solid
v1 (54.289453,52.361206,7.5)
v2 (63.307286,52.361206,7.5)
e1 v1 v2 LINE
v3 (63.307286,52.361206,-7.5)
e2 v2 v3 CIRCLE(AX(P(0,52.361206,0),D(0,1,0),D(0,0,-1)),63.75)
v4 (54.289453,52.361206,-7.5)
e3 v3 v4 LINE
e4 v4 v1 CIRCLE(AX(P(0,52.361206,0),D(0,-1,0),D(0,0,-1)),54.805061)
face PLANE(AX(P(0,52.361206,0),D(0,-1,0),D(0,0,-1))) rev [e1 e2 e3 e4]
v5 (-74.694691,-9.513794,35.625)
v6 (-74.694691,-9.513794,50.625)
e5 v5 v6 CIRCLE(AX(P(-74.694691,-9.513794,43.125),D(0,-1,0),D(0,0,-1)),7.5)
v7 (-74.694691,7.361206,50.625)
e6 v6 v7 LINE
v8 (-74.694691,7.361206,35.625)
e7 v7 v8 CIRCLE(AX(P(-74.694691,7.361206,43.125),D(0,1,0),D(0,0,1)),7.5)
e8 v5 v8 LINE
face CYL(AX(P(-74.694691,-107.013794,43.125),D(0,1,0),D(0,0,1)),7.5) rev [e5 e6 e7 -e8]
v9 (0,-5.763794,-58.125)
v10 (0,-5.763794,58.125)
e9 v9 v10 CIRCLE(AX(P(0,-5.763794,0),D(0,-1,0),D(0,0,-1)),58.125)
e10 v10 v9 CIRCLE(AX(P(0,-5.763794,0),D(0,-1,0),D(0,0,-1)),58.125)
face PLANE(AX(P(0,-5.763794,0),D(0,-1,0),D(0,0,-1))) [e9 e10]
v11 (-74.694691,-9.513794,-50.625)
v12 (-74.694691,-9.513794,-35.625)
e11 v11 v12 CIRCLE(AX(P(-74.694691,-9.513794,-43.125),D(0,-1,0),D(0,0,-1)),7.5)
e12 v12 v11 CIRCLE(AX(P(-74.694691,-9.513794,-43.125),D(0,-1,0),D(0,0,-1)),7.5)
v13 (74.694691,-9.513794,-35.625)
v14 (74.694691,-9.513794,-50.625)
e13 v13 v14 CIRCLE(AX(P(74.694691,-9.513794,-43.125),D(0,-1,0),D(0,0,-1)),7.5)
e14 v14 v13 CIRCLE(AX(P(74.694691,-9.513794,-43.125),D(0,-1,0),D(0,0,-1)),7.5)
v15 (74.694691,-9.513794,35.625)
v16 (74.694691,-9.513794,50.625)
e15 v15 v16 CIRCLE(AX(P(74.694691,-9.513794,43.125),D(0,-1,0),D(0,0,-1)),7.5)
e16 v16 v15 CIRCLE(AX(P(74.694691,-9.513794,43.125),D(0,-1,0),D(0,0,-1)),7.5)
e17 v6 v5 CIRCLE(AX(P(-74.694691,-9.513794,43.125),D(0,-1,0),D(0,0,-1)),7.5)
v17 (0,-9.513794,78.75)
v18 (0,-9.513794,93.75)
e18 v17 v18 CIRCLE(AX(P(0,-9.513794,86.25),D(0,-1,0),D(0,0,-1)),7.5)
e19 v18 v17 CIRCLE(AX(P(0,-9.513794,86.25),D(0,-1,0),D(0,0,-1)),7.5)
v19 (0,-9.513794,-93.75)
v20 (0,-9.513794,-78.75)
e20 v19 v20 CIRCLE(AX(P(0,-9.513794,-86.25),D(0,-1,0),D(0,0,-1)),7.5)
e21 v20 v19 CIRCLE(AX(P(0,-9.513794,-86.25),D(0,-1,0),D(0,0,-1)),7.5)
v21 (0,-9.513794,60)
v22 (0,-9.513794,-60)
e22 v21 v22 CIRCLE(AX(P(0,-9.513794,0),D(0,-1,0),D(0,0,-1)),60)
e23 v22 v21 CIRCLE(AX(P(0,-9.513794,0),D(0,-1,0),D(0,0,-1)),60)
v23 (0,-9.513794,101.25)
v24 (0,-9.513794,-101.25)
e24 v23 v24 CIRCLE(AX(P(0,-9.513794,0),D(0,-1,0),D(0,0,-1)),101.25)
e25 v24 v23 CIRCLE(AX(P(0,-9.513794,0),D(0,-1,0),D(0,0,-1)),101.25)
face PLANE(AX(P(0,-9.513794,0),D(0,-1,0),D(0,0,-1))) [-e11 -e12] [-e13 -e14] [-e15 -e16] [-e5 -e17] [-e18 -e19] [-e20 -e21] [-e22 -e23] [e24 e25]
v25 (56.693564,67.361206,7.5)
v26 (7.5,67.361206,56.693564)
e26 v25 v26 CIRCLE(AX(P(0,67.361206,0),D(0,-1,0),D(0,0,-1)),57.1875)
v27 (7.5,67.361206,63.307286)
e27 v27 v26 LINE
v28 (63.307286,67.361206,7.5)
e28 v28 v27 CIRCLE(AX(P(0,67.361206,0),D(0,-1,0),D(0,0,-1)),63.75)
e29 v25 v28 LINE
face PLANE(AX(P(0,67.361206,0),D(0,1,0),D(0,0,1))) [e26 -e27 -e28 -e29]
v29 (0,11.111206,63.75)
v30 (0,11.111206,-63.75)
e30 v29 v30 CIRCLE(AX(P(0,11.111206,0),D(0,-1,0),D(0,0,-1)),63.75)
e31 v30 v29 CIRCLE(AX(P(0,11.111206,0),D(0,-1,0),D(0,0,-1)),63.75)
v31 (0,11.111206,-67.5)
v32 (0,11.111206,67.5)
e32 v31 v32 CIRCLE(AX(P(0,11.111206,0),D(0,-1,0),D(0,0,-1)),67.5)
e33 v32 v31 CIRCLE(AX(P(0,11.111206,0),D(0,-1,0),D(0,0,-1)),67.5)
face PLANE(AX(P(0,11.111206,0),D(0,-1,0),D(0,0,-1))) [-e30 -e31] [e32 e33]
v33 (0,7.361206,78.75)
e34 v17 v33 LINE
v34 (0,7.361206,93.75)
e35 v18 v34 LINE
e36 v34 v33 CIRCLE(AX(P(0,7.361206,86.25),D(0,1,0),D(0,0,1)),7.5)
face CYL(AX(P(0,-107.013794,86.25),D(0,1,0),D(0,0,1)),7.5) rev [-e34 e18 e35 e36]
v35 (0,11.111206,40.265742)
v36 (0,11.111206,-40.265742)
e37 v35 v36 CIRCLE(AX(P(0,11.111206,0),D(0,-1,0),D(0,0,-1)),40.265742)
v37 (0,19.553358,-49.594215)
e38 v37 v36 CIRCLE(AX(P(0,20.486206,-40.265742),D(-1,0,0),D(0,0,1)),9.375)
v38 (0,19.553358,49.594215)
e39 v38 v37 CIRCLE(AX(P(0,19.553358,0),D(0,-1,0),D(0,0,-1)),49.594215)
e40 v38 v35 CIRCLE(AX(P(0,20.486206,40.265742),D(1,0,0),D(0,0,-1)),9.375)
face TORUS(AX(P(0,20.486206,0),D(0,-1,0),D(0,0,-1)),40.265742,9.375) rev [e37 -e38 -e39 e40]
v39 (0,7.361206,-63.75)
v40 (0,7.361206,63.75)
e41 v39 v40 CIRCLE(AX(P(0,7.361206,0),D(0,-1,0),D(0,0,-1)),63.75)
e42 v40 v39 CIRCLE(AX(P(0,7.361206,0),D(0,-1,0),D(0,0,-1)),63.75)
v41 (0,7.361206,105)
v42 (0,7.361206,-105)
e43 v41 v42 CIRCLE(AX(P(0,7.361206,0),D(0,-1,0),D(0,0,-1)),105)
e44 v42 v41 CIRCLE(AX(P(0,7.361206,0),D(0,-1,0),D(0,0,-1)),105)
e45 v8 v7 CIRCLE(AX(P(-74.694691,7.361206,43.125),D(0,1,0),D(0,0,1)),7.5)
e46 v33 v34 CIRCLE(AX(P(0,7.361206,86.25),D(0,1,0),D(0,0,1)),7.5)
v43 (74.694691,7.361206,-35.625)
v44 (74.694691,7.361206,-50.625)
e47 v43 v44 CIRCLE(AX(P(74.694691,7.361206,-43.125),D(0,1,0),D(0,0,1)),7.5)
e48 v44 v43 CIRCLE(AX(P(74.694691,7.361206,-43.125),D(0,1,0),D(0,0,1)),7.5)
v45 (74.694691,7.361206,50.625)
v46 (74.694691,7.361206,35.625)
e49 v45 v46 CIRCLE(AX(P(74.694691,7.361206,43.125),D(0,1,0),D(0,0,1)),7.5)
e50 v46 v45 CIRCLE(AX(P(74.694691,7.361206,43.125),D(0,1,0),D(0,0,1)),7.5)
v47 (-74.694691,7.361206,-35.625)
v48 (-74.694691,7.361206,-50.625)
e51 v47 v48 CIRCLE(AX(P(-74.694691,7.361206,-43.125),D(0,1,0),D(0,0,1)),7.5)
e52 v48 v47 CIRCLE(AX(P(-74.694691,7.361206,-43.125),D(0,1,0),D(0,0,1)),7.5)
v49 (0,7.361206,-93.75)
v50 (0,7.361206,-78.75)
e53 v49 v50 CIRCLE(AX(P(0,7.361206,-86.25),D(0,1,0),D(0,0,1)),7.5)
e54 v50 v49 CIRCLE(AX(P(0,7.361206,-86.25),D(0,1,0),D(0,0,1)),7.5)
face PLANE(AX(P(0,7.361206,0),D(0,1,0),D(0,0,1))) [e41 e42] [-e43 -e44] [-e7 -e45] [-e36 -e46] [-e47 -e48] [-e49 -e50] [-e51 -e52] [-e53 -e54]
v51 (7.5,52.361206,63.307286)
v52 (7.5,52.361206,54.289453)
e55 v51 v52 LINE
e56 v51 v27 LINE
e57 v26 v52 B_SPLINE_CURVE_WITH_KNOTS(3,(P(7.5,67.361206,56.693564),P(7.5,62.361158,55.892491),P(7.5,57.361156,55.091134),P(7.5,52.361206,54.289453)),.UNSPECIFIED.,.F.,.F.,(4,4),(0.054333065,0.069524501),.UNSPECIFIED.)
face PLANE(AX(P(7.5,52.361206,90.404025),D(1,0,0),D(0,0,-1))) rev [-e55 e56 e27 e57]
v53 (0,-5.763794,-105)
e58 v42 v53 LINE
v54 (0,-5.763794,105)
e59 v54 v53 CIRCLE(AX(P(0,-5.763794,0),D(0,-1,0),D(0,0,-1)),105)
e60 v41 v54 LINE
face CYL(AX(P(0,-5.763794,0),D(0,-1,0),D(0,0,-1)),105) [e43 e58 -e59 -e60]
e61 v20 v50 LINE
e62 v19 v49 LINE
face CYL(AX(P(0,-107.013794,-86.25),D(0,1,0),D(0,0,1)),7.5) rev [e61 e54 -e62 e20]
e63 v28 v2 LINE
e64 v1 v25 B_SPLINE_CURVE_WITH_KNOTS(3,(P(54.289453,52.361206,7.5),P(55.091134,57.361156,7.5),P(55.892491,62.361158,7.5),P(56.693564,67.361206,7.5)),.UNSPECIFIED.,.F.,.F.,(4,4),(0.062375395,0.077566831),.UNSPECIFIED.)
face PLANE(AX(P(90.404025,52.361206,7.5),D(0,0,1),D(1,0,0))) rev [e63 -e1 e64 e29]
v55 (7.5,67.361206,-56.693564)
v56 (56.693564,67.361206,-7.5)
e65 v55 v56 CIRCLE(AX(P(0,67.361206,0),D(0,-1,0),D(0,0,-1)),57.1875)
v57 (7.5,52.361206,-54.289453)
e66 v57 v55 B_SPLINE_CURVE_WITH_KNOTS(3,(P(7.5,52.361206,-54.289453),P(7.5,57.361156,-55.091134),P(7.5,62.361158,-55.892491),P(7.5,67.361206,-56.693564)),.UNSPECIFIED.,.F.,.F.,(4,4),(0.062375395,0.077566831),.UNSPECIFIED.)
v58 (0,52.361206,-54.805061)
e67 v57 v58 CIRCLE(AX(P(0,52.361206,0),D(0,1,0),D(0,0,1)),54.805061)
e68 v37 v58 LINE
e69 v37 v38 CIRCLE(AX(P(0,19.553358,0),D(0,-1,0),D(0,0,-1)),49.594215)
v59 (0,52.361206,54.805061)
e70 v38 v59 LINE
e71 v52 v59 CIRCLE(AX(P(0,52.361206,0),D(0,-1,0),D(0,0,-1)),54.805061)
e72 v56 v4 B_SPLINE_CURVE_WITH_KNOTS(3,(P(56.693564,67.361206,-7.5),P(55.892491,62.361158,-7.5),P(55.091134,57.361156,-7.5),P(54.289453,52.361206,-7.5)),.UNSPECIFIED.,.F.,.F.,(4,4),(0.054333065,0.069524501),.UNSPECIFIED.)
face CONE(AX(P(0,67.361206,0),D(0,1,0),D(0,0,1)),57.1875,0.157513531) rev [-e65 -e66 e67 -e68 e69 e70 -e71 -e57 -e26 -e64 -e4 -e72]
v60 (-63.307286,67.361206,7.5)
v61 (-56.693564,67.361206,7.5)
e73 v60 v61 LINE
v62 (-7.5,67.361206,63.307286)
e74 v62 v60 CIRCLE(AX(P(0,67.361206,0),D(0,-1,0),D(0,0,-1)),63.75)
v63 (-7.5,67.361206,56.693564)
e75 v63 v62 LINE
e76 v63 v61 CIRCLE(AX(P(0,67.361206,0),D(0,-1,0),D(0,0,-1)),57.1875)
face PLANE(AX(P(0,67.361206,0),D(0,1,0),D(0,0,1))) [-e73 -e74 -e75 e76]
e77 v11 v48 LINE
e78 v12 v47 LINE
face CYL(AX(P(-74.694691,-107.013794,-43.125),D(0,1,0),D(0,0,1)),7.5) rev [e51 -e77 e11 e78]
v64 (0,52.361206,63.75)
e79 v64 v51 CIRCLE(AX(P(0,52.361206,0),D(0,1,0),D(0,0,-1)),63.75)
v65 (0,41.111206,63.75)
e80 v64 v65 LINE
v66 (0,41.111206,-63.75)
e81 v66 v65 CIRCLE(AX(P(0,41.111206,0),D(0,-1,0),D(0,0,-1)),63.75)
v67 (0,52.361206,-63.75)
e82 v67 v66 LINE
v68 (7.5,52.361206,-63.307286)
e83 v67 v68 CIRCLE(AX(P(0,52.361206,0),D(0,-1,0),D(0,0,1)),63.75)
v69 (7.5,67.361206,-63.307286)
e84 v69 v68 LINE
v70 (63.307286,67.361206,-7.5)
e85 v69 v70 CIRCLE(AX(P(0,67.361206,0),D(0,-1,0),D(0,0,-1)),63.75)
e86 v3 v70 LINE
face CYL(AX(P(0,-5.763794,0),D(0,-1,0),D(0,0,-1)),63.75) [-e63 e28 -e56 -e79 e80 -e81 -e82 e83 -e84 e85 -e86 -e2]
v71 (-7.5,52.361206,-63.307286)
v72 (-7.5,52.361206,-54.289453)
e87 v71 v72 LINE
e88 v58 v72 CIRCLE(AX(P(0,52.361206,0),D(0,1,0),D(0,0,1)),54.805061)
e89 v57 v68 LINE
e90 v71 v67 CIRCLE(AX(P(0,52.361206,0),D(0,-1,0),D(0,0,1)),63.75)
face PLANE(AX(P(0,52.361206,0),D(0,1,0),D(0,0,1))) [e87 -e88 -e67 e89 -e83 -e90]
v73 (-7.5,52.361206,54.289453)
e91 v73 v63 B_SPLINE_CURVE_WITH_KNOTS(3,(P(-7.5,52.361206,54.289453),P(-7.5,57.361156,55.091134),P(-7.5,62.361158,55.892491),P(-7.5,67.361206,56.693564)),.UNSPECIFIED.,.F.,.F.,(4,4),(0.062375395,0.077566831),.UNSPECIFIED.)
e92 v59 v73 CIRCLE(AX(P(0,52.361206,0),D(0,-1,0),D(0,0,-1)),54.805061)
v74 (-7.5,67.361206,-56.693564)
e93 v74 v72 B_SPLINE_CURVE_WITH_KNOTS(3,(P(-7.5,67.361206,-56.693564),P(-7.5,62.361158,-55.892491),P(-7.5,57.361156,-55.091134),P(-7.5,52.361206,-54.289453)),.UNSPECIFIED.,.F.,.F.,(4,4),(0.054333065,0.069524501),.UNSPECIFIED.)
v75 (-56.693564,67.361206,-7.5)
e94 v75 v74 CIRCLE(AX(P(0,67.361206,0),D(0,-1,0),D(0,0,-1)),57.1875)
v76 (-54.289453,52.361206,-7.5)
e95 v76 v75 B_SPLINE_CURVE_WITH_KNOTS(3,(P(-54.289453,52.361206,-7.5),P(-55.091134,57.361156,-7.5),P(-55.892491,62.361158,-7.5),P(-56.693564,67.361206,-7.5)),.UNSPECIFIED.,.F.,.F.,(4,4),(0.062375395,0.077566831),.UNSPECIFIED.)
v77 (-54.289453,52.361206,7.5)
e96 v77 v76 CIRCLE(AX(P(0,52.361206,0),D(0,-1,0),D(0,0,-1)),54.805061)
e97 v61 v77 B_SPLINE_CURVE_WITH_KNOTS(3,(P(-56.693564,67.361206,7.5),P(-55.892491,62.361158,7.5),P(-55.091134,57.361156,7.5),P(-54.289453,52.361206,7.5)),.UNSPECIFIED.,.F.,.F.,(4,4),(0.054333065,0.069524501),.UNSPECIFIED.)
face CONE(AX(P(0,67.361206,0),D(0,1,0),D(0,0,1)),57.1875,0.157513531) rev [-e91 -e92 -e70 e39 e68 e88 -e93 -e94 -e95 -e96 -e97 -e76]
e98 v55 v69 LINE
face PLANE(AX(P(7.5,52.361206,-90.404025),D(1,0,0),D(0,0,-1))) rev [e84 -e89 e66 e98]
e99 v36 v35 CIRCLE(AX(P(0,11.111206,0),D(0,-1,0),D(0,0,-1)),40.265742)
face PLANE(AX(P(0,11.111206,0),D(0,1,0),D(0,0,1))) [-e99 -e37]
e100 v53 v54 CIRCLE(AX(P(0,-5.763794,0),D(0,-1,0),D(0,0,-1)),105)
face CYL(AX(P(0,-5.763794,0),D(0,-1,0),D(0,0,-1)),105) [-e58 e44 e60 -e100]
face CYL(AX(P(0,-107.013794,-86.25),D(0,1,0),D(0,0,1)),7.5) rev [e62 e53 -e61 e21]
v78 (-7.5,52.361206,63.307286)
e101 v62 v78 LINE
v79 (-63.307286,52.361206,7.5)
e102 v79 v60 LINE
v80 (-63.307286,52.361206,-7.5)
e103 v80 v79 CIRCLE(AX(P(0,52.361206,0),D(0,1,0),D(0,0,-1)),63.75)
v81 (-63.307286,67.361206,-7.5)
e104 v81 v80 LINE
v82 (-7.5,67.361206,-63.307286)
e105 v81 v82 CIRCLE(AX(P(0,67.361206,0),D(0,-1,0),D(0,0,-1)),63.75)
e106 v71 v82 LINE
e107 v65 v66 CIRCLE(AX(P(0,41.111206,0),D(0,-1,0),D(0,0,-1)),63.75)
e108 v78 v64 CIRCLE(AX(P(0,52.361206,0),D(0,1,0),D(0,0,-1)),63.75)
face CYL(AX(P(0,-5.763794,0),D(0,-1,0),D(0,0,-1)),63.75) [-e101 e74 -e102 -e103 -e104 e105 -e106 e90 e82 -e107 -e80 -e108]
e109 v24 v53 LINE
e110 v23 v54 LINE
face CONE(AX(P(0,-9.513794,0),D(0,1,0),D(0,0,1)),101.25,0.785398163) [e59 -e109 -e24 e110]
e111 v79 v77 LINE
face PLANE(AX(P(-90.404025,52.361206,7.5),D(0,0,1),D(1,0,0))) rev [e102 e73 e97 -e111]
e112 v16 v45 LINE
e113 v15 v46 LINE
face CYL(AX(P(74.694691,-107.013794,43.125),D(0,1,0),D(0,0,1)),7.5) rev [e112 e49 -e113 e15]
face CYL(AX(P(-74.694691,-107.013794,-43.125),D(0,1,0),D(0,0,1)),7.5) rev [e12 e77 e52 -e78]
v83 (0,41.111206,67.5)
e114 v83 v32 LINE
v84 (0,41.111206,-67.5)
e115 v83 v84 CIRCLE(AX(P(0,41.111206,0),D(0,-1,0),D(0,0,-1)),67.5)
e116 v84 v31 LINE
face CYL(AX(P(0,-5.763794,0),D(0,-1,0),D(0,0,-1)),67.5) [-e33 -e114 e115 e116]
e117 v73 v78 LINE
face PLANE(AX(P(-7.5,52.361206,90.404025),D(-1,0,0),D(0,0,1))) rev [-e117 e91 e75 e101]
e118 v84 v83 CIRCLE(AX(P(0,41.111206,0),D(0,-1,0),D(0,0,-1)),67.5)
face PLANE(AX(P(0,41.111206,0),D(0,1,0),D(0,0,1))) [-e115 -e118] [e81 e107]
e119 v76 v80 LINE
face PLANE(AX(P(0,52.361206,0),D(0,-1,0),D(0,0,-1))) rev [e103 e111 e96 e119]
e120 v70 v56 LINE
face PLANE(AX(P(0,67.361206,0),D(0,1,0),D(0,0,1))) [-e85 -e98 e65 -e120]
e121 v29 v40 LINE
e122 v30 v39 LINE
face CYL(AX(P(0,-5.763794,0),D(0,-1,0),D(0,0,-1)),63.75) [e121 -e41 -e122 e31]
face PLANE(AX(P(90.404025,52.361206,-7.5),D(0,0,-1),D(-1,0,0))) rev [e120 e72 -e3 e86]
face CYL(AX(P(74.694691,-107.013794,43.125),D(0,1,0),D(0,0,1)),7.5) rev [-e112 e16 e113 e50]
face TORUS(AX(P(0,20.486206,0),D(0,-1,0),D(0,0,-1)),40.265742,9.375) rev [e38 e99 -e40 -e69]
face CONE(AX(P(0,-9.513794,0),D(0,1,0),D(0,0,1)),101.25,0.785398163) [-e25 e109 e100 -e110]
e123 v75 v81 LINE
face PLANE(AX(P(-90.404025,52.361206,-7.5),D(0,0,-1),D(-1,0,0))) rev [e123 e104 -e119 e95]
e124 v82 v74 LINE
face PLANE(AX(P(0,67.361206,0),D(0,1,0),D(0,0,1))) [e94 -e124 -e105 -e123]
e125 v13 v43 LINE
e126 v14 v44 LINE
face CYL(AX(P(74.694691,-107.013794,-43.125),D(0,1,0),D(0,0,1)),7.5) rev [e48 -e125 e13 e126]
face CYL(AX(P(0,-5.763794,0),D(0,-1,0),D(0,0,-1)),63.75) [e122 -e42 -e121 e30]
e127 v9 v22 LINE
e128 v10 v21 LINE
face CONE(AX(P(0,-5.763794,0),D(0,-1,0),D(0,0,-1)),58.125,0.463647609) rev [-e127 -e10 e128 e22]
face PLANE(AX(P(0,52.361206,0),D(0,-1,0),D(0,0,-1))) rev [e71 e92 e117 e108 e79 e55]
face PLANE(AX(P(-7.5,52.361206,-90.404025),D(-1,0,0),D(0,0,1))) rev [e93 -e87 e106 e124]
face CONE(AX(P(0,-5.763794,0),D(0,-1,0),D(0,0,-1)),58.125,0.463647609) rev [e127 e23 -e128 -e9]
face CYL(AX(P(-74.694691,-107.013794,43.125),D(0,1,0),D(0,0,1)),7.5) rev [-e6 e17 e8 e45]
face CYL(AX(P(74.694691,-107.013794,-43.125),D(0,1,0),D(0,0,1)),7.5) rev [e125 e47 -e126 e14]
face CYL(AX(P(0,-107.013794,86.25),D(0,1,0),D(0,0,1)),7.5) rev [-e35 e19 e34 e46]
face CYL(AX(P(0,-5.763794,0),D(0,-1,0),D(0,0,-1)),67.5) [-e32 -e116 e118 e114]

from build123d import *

# Parameters (mm, degrees)
SKETCH2_W          = 33.532576539
SKETCH2_H          = 8
SKETCH2_W_2        = 8
SKETCH2_H_2        = 33.532576539
CUT_EXTRUDE1_DEPTH = 8
SKETCH3_R          = 4
CUT_EXTRUDE2_DEPTH = 93
SCALE_1_SCALE      = 1.875


with BuildPart() as part:
    # Sketch1 → Revolve1 (revolve)
    with BuildSketch(Plane.XY, mode=Mode.PRIVATE) as revolve1_sk:
        with BuildLine():
            Line((0, 11), (0, 2))
            Line((0, 2), (31, 2))
            Line((31, 2), (32, 0))
            Line((32, 0), (54, 0))
            Line((54, 0), (56, 2))
            Line((56, 2), (56, 9))
            Line((56, 9), (34, 9))
            Line((34, 9), (34, 11))
            Line((34, 11), (36, 11))
            Line((36, 11), (36, 27))
            Line((36, 27), (34, 27))
            Line((34, 27), (34, 41))
            Line((34, 41), (30.5, 41))
            Line((30.5, 41), (26.45024814, 15.502481405))
            ThreePointArc((26.45024814, 15.502481405), (24.830088793, 12.292737332), (21.475062189, 11))
            Line((21.475062189, 11), (16.570568921, 11))
            Line((16.570568921, 11), (0, 11))
        make_face()
    revolve(revolve1_sk.sketch.rotate(Axis((0, 2, 0), (0, 1, 0)), 90), axis=Axis((0, 2, 0), (0, 1, 0)))

    # Sketch2 → Cut-Extrude1 (cut)
    with BuildSketch(Plane(origin=(0, 41, 0), x_dir=(1, 0, 0), z_dir=(0, 1, 0))):
        with Locations((31.449191607, 0)):
            Rectangle(SKETCH2_W, SKETCH2_H)
        with Locations((0, 31.449191607)):
            Rectangle(SKETCH2_W_2, SKETCH2_H_2)
        with Locations((0, -31.449191607)):
            Rectangle(SKETCH2_W_2, SKETCH2_H_2)
        with Locations((-31.449191607, 0)):
            Rectangle(SKETCH2_W, SKETCH2_H)
    extrude(amount=-CUT_EXTRUDE1_DEPTH, mode=Mode.SUBTRACT)

    # Sketch3 → Cut-Extrude2 (cut)
    with BuildSketch(Plane(origin=(0, 41, 0), x_dir=(1, 0, 0), z_dir=(0, 1, 0))):
        with Locations(Location((-39.837168574, -23, 0), (0, 0, 270))):
            Circle(SKETCH3_R)
        with Locations(Location((0, 46, 0), (0, 0, 270))):
            Circle(SKETCH3_R)
        with Locations(Location((39.837168574, 23, 0), (0, 0, 270))):
            Circle(SKETCH3_R)
        with Locations(Location((-39.837168574, 23, 0), (0, 0, 270))):
            Circle(SKETCH3_R)
        with Locations(Location((0, -46, 0), (0, 0, 270))):
            Circle(SKETCH3_R)
        with Locations(Location((39.837168574, -23, 0), (0, 0, 270))):
            Circle(SKETCH3_R)
    extrude(amount=-CUT_EXTRUDE2_DEPTH, mode=Mode.SUBTRACT)


with BuildPart() as part_1:
    # Scale 1: scaled about (0, 10.8729077, 0)
    add(part.part.scale(SCALE_1_SCALE).moved(Location((0, -9.513794238, 0))))


solid = part_1.part
